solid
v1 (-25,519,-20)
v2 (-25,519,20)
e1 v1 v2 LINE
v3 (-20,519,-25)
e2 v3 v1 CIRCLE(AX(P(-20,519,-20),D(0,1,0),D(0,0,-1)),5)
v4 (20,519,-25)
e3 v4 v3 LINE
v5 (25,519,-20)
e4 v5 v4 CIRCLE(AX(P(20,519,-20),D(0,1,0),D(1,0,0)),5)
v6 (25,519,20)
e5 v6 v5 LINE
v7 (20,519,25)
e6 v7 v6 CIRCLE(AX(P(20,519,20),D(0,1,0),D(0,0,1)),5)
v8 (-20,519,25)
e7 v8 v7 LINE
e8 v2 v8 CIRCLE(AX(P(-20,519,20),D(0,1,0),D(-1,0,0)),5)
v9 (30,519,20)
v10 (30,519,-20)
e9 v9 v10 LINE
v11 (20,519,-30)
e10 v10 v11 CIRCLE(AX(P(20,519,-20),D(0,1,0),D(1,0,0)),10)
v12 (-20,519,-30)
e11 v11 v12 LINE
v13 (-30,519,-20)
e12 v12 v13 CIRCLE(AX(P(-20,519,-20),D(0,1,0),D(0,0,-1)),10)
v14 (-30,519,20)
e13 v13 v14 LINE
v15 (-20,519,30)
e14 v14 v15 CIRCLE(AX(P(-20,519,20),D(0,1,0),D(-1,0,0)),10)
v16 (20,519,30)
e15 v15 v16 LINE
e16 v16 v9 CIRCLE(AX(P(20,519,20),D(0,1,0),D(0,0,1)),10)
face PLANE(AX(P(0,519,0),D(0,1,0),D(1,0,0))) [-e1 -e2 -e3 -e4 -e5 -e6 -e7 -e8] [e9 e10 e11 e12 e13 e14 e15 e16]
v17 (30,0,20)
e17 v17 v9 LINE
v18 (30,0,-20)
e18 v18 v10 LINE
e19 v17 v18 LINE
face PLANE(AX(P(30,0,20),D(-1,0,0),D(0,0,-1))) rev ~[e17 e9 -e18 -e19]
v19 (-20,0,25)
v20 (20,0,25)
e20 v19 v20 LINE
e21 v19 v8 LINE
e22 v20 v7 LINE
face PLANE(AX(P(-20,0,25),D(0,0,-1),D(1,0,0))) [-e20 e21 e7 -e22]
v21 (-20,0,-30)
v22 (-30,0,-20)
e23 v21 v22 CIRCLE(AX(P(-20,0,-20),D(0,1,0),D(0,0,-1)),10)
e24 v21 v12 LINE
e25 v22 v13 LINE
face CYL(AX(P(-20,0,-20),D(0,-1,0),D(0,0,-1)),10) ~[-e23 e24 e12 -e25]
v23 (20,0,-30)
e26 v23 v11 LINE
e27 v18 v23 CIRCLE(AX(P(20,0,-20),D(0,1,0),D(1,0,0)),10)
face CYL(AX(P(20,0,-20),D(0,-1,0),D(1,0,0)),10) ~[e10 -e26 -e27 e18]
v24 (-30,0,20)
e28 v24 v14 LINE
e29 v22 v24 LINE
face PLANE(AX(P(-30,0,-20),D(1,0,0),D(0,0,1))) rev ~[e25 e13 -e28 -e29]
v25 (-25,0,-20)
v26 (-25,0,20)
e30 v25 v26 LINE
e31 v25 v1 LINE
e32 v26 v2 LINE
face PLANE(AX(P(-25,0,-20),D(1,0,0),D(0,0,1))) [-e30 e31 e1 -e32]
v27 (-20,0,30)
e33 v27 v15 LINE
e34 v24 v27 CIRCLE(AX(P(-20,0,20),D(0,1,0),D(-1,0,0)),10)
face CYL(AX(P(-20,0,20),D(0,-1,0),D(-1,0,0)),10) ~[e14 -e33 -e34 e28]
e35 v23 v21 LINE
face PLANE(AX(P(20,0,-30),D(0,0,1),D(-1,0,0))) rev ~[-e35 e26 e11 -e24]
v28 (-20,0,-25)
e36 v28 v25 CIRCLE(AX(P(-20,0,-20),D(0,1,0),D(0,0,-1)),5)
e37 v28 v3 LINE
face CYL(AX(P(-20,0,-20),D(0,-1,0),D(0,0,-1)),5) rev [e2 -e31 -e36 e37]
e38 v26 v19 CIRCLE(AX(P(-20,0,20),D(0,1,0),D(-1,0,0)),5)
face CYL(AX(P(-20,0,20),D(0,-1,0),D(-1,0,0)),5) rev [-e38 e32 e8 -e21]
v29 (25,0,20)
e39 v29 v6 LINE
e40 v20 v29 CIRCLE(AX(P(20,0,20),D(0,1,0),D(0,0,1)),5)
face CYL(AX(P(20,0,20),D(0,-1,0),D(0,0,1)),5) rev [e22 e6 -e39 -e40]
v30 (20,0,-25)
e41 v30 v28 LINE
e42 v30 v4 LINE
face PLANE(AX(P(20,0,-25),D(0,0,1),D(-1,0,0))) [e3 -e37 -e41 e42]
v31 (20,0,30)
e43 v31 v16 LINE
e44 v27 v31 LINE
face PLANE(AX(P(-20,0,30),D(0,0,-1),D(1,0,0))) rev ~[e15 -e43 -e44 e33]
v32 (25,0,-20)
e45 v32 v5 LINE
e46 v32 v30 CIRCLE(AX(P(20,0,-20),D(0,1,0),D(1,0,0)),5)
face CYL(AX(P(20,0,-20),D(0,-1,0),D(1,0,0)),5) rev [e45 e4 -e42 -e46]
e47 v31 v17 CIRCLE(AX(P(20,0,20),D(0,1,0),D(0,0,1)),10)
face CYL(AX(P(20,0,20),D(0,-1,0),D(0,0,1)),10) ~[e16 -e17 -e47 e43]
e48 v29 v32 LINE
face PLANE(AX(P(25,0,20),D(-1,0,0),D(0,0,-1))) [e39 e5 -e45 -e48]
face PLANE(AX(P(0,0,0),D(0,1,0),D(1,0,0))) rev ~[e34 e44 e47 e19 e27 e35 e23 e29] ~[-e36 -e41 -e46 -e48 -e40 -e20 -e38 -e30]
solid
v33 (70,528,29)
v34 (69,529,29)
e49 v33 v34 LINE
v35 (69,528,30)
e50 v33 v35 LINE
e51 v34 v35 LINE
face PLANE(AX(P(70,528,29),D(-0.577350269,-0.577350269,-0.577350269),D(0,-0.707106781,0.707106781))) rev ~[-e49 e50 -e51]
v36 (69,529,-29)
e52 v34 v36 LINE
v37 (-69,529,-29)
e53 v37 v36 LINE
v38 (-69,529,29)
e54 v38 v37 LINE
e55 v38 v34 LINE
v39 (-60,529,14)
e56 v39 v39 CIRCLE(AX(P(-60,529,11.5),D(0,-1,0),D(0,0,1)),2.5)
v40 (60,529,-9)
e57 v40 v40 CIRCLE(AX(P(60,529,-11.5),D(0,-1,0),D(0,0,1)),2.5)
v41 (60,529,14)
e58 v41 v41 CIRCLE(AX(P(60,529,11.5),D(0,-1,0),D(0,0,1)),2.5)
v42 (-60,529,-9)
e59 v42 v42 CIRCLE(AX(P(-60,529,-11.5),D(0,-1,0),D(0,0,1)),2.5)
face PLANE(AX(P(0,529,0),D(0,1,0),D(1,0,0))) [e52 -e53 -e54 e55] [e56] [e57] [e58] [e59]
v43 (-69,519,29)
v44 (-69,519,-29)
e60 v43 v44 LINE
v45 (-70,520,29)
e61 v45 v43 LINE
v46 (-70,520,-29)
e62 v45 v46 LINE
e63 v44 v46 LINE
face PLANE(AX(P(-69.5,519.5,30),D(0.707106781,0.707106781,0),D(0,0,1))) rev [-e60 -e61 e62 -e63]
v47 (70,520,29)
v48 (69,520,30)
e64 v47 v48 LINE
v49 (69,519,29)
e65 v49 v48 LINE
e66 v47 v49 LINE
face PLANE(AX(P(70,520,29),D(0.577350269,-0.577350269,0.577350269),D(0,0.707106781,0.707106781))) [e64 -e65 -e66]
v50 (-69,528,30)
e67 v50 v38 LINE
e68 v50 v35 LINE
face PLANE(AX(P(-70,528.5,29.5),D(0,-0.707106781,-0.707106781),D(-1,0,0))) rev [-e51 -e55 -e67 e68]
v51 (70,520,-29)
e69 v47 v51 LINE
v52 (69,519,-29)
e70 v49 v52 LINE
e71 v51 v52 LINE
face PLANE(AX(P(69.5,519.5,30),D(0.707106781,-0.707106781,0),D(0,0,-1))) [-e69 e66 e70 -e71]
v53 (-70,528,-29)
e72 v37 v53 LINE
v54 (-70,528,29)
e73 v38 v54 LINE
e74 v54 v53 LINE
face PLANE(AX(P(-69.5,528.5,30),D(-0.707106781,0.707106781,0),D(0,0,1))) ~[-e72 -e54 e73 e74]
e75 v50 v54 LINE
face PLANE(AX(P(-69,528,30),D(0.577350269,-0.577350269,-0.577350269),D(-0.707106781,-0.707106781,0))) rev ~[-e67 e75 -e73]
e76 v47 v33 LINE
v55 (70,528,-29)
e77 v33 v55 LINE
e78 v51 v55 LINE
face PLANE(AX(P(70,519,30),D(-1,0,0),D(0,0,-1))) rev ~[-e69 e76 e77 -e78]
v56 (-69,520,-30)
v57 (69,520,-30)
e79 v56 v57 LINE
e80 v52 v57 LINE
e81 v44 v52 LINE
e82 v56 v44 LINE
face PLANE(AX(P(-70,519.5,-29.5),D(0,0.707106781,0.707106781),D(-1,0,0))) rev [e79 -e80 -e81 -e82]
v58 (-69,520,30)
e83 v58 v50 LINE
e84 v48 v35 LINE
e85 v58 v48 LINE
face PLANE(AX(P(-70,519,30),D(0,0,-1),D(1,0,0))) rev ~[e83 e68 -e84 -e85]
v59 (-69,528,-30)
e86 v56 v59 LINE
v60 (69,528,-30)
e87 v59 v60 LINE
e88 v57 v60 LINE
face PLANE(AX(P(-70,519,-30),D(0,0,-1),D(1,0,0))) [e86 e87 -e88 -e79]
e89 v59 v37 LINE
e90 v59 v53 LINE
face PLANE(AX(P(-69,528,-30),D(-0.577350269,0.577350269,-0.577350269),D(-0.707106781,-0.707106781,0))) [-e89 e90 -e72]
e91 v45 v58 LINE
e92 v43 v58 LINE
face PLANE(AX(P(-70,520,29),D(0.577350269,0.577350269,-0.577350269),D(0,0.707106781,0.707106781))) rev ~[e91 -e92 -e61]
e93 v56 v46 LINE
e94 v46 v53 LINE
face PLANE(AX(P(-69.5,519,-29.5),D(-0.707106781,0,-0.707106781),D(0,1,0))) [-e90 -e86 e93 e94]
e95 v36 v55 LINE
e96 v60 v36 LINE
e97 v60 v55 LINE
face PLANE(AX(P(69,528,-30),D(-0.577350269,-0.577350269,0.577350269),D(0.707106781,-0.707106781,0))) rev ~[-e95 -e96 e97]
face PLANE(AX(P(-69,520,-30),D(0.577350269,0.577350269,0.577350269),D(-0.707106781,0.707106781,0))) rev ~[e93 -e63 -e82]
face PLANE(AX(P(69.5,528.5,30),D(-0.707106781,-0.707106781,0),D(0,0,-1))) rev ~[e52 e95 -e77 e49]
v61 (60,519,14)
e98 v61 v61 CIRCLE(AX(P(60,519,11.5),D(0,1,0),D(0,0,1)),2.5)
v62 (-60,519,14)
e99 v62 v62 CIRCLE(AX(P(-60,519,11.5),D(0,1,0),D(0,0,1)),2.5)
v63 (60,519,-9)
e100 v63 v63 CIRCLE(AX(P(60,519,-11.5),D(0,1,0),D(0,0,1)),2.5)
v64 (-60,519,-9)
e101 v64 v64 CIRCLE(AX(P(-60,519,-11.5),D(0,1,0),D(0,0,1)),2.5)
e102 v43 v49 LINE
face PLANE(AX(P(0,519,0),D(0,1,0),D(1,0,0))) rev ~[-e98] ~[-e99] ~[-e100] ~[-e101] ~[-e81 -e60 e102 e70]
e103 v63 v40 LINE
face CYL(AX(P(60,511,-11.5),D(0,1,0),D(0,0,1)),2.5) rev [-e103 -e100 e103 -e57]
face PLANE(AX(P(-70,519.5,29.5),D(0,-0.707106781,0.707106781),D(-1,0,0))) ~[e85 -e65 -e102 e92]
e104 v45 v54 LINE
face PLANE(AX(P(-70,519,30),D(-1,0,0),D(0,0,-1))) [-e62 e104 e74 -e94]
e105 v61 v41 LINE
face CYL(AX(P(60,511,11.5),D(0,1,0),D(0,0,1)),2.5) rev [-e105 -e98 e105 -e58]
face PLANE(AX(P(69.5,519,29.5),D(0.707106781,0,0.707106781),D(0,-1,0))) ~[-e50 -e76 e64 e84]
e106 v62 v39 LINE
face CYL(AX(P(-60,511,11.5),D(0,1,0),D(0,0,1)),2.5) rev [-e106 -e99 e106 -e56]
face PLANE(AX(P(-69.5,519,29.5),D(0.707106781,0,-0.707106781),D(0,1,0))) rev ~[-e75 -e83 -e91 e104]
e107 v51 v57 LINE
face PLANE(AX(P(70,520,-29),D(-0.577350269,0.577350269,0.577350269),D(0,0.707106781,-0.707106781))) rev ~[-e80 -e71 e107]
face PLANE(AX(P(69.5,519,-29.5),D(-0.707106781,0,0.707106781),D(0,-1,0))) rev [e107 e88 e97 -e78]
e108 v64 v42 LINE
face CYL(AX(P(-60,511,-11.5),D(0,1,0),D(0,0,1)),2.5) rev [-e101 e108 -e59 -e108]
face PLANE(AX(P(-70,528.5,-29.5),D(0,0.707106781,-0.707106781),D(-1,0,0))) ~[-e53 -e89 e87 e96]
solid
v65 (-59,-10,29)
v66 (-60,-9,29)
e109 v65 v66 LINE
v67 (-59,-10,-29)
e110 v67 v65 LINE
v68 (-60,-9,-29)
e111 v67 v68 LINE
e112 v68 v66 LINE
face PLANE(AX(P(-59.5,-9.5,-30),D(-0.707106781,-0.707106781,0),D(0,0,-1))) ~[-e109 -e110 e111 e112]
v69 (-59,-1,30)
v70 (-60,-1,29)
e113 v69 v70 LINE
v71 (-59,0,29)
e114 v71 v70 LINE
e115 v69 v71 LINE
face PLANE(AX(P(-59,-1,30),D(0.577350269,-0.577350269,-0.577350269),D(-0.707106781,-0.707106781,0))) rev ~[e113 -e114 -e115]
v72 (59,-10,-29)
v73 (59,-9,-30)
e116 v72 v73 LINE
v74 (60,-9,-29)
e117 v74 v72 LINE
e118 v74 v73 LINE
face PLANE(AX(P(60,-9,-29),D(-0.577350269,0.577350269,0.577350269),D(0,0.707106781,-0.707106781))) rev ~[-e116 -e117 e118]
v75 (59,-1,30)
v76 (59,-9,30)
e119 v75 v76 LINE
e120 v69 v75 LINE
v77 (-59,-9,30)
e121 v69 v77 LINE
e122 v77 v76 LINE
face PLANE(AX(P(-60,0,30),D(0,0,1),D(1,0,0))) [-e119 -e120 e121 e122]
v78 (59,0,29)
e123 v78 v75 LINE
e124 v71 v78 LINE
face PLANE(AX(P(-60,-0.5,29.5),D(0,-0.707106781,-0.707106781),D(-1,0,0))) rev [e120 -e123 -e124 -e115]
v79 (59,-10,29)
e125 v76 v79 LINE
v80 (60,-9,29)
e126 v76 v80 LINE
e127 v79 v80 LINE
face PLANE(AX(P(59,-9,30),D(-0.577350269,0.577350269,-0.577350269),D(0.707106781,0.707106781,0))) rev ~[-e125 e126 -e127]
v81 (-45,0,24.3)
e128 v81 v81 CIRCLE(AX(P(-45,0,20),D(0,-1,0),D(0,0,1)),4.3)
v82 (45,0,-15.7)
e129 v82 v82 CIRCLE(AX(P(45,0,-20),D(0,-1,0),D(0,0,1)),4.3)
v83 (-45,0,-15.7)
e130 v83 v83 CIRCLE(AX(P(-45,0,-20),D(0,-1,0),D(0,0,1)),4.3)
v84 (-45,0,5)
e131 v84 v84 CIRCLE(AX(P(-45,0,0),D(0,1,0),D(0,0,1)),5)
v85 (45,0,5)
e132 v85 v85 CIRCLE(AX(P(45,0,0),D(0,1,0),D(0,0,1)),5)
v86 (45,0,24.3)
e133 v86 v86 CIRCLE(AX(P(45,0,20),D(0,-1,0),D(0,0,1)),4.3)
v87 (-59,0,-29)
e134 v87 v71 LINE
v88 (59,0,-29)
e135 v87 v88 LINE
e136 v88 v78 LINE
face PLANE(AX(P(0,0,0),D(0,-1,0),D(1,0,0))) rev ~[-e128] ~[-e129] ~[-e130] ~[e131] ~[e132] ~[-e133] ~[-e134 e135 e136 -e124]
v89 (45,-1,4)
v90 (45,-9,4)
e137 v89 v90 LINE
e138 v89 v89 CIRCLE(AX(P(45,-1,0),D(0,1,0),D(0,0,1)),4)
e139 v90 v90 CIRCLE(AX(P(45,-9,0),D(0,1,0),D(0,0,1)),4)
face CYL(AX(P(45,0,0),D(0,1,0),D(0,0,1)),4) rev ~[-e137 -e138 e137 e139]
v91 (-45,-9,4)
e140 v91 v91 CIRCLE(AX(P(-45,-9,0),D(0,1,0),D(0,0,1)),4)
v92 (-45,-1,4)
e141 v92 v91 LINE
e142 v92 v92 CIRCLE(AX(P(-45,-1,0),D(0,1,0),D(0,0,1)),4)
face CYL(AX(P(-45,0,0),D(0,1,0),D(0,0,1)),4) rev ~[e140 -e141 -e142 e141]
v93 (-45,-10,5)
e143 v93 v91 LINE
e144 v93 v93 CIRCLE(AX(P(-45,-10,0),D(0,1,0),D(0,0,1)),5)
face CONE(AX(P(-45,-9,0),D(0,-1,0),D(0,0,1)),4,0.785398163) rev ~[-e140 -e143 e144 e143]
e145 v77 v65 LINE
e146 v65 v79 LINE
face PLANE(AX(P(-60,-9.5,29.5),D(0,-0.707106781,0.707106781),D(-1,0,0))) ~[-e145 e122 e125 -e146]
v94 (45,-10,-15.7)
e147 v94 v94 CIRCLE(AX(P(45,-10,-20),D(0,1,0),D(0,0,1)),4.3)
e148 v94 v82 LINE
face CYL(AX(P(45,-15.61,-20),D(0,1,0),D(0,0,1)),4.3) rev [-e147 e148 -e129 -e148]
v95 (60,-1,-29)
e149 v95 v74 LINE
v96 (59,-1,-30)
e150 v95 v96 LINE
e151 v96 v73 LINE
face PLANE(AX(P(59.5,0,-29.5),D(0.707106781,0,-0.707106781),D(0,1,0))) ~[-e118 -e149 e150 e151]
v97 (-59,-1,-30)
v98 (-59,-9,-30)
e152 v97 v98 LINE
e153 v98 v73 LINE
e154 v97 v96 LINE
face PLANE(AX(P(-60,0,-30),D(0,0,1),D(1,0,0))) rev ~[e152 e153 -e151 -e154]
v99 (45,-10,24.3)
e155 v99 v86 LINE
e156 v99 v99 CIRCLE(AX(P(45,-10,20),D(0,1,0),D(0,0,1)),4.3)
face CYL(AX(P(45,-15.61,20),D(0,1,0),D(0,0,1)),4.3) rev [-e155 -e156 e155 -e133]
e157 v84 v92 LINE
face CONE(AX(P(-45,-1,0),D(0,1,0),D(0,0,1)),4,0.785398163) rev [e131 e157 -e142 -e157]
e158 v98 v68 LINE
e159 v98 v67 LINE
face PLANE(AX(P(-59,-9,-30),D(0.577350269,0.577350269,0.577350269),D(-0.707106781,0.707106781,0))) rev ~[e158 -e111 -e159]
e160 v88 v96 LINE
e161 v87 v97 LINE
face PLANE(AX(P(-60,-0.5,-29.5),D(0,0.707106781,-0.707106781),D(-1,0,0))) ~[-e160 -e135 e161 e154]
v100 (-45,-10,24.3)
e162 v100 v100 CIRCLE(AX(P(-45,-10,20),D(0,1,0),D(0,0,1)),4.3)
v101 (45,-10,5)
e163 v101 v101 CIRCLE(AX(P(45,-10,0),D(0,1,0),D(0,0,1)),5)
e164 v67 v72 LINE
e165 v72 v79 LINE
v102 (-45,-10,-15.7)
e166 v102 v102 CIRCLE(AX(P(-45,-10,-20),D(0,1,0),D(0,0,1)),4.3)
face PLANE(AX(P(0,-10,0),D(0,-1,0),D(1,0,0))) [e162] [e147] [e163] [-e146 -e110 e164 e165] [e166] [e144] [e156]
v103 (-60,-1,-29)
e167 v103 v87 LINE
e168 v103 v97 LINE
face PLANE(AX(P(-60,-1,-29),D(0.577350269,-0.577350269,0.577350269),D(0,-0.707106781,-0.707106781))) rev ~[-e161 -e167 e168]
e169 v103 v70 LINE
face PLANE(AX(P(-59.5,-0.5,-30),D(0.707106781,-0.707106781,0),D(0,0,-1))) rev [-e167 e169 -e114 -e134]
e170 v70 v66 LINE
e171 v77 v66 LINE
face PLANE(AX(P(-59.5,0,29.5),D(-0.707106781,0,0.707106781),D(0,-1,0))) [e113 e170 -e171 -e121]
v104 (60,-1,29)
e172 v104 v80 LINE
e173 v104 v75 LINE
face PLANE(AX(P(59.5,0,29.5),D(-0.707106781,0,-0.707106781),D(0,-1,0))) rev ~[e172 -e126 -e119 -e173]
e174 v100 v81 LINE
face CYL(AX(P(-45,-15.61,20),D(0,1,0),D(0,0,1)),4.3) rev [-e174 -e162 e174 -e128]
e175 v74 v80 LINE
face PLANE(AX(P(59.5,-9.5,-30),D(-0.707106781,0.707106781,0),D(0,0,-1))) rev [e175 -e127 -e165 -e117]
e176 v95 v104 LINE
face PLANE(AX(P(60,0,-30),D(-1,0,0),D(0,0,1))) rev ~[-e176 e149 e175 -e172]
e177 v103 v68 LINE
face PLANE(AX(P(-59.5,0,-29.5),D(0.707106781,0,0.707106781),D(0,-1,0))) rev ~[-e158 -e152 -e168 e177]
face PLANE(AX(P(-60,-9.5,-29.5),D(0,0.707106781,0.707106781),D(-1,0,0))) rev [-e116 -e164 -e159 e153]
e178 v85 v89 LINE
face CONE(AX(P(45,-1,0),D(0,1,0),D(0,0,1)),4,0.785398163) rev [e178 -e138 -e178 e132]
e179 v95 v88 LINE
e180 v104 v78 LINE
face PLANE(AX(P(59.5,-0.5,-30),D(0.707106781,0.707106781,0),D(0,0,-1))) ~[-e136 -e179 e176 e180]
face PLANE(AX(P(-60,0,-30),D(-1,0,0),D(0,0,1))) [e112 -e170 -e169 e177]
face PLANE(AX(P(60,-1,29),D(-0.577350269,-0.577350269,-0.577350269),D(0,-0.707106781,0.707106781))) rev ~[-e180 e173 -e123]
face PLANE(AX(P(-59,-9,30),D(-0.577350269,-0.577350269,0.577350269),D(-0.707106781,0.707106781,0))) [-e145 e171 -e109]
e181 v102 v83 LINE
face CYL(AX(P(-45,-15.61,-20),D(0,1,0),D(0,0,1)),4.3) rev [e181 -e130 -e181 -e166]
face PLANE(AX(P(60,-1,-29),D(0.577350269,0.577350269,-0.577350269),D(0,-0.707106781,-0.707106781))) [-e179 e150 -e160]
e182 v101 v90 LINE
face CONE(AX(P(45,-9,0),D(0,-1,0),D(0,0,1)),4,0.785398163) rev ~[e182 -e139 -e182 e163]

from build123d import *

# Parameters (mm, degrees)
MEMBER_1_DEPTH                   = 519
SKETCH_2_W                       = 140
SKETCH_2_H                       = 60
EXTRUDE_1_DEPTH                  = 10
SKETCH_3_W                       = 120
SKETCH_3_H                       = 60
EXTRUDE_2_DEPTH                  = 10
HOLE_WIZARD_0_AT_2_COUNT         = 2
HOLE_WIZARD_0_AT_2_PITCH         = 120
HOLE_WIZARD_0_AT_3_COUNT         = 2
HOLE_WIZARD_0_AT_3_PITCH         = 122.184287042
HOLE_WIZARD_0_AT_4_COUNT         = 2
HOLE_WIZARD_0_AT_4_PITCH         = 23
CHAMFER_1_SIZE                   = 1
CHAMFER_2_SIZE                   = 1
HOLE_WIZARD_8_6_8_6_1_AT_2_COUNT = 2
HOLE_WIZARD_8_6_8_6_1_AT_2_PITCH = 40
HOLE_WIZARD_8_6_8_6_1_AT_3_COUNT = 2
HOLE_WIZARD_8_6_8_6_1_AT_3_PITCH = 90
HOLE_WIZARD_8_6_8_6_1_AT_4_COUNT = 2
HOLE_WIZARD_8_6_8_6_1_AT_4_PITCH = 98.488578018
SKETCH_9_R                       = 4
CUT_EXTRUDE_1_DEPTH              = 535.45392692
CHAMFER_3_SIZE                   = 1


with BuildPart() as part:
    # Sketch11 → Member 1 (new body)
    with BuildSketch(Plane(origin=(0, 0, 0), x_dir=(1, 0, 0), z_dir=(0, 1, 0))):
        with BuildLine():
            Line((-20, -30), (20, -30))
            ThreePointArc((20, -30), (27.071067812, -27.071067812), (30, -20))
            Line((30, -20), (30, 20))
            ThreePointArc((30, 20), (27.071067812, 27.071067812), (20, 30))
            Line((20, 30), (-20, 30))
            ThreePointArc((-20, 30), (-27.071067812, 27.071067812), (-30, 20))
            Line((-30, 20), (-30, -20))
            ThreePointArc((-30, -20), (-27.071067812, -27.071067812), (-20, -30))
        make_face()
        with BuildLine():
            Line((-20, -25), (20, -25))
            ThreePointArc((20, -25), (23.535533906, -23.535533906), (25, -20))
            Line((25, -20), (25, 20))
            ThreePointArc((25, 20), (23.535533906, 23.535533906), (20, 25))
            Line((20, 25), (-20, 25))
            ThreePointArc((-20, 25), (-23.535533906, 23.535533906), (-25, 20))
            Line((-25, 20), (-25, -20))
            ThreePointArc((-25, -20), (-23.535533906, -23.535533906), (-20, -25))
        make_face(mode=Mode.SUBTRACT)
    extrude(amount=MEMBER_1_DEPTH)


with BuildPart() as body_2:
    # 草图2 → 凸台-拉伸1 (new body)
    with BuildSketch(Plane(origin=(0, 519, 0), x_dir=(1, 0, 0), z_dir=(0, 1, 0))):
        Rectangle(SKETCH_2_W, SKETCH_2_H)
    extrude(amount=EXTRUDE_1_DEPTH)

    # 草图4 → Hole Wizard 0 (revolve, cut)
    with BuildSketch(Plane(origin=(60, 529, -11.5), x_dir=(0, 0, 1), z_dir=(1, 0, 0))):
        Polygon((0, 0), (0, 19.502151548), (2.5, 18), (2.5, 0), align=None)
    hole_wizard_0 = revolve(axis=Axis((60, 535.35, -11.5), (0, -1, 0)), mode=Mode.SUBTRACT)

    # Hole Wizard 0 at 2: Hole Wizard 0 ×2
    with Locations(*[(-i * HOLE_WIZARD_0_AT_2_PITCH, 0, 0) for i in range(1, HOLE_WIZARD_0_AT_2_COUNT)]):
        add(hole_wizard_0, mode=Mode.SUBTRACT)

    # Hole Wizard 0 at 3: Hole Wizard 0 ×2
    with Locations(*[Vector(-0.982123011927037, 0, 0.1882402439526821) * (i * HOLE_WIZARD_0_AT_3_PITCH) for i in range(1, HOLE_WIZARD_0_AT_3_COUNT)]):
        add(hole_wizard_0, mode=Mode.SUBTRACT)

    # Hole Wizard 0 at 4: Hole Wizard 0 ×2
    with Locations(*[(0, 0, i * HOLE_WIZARD_0_AT_4_PITCH) for i in range(1, HOLE_WIZARD_0_AT_4_COUNT)]):
        add(hole_wizard_0, mode=Mode.SUBTRACT)

    # 倒角2
    chamfer_2_edges = [body_2.edges().sort_by_distance(p)[0] for p in [
        (-70, 529, 0),
        (0, 529, 30),
        (70, 529, 0),
        (0, 519, 30),
        (-70, 519, 0),
        (0, 519, -30),
        (70, 519, 0),
        (0, 529, -30),
        (70, 524, 30),
        (-70, 524, 30),
        (-70, 524, -30),
        (70, 524, -30),
    ]]
    chamfer(chamfer_2_edges, length=CHAMFER_2_SIZE)


with BuildPart() as body_3:
    # 草图3 → 凸台-拉伸2 (new body)
    with BuildSketch(Plane.XZ):
        Rectangle(SKETCH_3_W, SKETCH_3_H)
    extrude(amount=EXTRUDE_2_DEPTH)

    # 倒角1
    chamfer_1_edges = [body_3.edges().sort_by_distance(p)[0] for p in [
        (-60, -10, 0),
        (0, -10, -30),
        (60, -10, 0),
        (0, 0, -30),
        (-60, 0, 0),
        (0, 0, 30),
        (60, 0, 0),
        (0, -10, 30),
        (60, -5, -30),
        (-60, -5, -30),
        (-60, -5, 30),
        (60, -5, 30),
    ]]
    chamfer(chamfer_1_edges, length=CHAMFER_1_SIZE)

    # 草图6 → Ø8.6 (8.6) 直径孔1 (revolve, cut)
    with BuildSketch(Plane(origin=(-45, 0, 20), x_dir=(0, 0, 1), z_dir=(1, 0, 0))):
        Polygon((0, 0), (0, 18.092606158), (4.3, 15.61), (4.3, 0), align=None)
    hole_wizard_8_6_8_6_1 = revolve(axis=Axis((-45, 6.35, 20), (0, -1, 0)), mode=Mode.SUBTRACT)

    # Ø8.6 (8.6) 直径孔1 at 2: Ø8.6 (8.6) 直径孔1 ×2
    with Locations(*[(0, 0, -i * HOLE_WIZARD_8_6_8_6_1_AT_2_PITCH) for i in range(1, HOLE_WIZARD_8_6_8_6_1_AT_2_COUNT)]):
        add(hole_wizard_8_6_8_6_1, mode=Mode.SUBTRACT)

    # Ø8.6 (8.6) 直径孔1 at 3: Ø8.6 (8.6) 直径孔1 ×2
    with Locations(*[(i * HOLE_WIZARD_8_6_8_6_1_AT_3_PITCH, 0, 0) for i in range(1, HOLE_WIZARD_8_6_8_6_1_AT_3_COUNT)]):
        add(hole_wizard_8_6_8_6_1, mode=Mode.SUBTRACT)

    # Ø8.6 (8.6) 直径孔1 at 4: Ø8.6 (8.6) 直径孔1 ×2
    with Locations(*[Vector(0.9138115486202572, 0, -0.4061384660534476) * (i * HOLE_WIZARD_8_6_8_6_1_AT_4_PITCH) for i in range(1, HOLE_WIZARD_8_6_8_6_1_AT_4_COUNT)]):
        add(hole_wizard_8_6_8_6_1, mode=Mode.SUBTRACT)

    # 草图9 → 切除-拉伸1 (cut, through all)
    with BuildSketch(Plane(origin=(0, 0, 0), x_dir=(1, 0, 0), z_dir=(0, 1, 0))):
        with Locations(Location((-45, 0, 0), (0, 0, 270))):
            Circle(SKETCH_9_R)
        with Locations(Location((45, 0, 0), (0, 0, 270))):
            Circle(SKETCH_9_R)
    extrude(amount=-CUT_EXTRUDE_1_DEPTH, mode=Mode.SUBTRACT)

    # 倒角3
    chamfer_3_edges = [body_3.edges().sort_by_distance(p)[0] for p in [
        (-45, -10, -4),
        (-45, 0, -4),
        (45, -10, -4),
        (45, 0, -4),
    ]]
    chamfer(chamfer_3_edges, length=CHAMFER_3_SIZE)


solid = Compound([part.part, body_2.part, body_3.part])
